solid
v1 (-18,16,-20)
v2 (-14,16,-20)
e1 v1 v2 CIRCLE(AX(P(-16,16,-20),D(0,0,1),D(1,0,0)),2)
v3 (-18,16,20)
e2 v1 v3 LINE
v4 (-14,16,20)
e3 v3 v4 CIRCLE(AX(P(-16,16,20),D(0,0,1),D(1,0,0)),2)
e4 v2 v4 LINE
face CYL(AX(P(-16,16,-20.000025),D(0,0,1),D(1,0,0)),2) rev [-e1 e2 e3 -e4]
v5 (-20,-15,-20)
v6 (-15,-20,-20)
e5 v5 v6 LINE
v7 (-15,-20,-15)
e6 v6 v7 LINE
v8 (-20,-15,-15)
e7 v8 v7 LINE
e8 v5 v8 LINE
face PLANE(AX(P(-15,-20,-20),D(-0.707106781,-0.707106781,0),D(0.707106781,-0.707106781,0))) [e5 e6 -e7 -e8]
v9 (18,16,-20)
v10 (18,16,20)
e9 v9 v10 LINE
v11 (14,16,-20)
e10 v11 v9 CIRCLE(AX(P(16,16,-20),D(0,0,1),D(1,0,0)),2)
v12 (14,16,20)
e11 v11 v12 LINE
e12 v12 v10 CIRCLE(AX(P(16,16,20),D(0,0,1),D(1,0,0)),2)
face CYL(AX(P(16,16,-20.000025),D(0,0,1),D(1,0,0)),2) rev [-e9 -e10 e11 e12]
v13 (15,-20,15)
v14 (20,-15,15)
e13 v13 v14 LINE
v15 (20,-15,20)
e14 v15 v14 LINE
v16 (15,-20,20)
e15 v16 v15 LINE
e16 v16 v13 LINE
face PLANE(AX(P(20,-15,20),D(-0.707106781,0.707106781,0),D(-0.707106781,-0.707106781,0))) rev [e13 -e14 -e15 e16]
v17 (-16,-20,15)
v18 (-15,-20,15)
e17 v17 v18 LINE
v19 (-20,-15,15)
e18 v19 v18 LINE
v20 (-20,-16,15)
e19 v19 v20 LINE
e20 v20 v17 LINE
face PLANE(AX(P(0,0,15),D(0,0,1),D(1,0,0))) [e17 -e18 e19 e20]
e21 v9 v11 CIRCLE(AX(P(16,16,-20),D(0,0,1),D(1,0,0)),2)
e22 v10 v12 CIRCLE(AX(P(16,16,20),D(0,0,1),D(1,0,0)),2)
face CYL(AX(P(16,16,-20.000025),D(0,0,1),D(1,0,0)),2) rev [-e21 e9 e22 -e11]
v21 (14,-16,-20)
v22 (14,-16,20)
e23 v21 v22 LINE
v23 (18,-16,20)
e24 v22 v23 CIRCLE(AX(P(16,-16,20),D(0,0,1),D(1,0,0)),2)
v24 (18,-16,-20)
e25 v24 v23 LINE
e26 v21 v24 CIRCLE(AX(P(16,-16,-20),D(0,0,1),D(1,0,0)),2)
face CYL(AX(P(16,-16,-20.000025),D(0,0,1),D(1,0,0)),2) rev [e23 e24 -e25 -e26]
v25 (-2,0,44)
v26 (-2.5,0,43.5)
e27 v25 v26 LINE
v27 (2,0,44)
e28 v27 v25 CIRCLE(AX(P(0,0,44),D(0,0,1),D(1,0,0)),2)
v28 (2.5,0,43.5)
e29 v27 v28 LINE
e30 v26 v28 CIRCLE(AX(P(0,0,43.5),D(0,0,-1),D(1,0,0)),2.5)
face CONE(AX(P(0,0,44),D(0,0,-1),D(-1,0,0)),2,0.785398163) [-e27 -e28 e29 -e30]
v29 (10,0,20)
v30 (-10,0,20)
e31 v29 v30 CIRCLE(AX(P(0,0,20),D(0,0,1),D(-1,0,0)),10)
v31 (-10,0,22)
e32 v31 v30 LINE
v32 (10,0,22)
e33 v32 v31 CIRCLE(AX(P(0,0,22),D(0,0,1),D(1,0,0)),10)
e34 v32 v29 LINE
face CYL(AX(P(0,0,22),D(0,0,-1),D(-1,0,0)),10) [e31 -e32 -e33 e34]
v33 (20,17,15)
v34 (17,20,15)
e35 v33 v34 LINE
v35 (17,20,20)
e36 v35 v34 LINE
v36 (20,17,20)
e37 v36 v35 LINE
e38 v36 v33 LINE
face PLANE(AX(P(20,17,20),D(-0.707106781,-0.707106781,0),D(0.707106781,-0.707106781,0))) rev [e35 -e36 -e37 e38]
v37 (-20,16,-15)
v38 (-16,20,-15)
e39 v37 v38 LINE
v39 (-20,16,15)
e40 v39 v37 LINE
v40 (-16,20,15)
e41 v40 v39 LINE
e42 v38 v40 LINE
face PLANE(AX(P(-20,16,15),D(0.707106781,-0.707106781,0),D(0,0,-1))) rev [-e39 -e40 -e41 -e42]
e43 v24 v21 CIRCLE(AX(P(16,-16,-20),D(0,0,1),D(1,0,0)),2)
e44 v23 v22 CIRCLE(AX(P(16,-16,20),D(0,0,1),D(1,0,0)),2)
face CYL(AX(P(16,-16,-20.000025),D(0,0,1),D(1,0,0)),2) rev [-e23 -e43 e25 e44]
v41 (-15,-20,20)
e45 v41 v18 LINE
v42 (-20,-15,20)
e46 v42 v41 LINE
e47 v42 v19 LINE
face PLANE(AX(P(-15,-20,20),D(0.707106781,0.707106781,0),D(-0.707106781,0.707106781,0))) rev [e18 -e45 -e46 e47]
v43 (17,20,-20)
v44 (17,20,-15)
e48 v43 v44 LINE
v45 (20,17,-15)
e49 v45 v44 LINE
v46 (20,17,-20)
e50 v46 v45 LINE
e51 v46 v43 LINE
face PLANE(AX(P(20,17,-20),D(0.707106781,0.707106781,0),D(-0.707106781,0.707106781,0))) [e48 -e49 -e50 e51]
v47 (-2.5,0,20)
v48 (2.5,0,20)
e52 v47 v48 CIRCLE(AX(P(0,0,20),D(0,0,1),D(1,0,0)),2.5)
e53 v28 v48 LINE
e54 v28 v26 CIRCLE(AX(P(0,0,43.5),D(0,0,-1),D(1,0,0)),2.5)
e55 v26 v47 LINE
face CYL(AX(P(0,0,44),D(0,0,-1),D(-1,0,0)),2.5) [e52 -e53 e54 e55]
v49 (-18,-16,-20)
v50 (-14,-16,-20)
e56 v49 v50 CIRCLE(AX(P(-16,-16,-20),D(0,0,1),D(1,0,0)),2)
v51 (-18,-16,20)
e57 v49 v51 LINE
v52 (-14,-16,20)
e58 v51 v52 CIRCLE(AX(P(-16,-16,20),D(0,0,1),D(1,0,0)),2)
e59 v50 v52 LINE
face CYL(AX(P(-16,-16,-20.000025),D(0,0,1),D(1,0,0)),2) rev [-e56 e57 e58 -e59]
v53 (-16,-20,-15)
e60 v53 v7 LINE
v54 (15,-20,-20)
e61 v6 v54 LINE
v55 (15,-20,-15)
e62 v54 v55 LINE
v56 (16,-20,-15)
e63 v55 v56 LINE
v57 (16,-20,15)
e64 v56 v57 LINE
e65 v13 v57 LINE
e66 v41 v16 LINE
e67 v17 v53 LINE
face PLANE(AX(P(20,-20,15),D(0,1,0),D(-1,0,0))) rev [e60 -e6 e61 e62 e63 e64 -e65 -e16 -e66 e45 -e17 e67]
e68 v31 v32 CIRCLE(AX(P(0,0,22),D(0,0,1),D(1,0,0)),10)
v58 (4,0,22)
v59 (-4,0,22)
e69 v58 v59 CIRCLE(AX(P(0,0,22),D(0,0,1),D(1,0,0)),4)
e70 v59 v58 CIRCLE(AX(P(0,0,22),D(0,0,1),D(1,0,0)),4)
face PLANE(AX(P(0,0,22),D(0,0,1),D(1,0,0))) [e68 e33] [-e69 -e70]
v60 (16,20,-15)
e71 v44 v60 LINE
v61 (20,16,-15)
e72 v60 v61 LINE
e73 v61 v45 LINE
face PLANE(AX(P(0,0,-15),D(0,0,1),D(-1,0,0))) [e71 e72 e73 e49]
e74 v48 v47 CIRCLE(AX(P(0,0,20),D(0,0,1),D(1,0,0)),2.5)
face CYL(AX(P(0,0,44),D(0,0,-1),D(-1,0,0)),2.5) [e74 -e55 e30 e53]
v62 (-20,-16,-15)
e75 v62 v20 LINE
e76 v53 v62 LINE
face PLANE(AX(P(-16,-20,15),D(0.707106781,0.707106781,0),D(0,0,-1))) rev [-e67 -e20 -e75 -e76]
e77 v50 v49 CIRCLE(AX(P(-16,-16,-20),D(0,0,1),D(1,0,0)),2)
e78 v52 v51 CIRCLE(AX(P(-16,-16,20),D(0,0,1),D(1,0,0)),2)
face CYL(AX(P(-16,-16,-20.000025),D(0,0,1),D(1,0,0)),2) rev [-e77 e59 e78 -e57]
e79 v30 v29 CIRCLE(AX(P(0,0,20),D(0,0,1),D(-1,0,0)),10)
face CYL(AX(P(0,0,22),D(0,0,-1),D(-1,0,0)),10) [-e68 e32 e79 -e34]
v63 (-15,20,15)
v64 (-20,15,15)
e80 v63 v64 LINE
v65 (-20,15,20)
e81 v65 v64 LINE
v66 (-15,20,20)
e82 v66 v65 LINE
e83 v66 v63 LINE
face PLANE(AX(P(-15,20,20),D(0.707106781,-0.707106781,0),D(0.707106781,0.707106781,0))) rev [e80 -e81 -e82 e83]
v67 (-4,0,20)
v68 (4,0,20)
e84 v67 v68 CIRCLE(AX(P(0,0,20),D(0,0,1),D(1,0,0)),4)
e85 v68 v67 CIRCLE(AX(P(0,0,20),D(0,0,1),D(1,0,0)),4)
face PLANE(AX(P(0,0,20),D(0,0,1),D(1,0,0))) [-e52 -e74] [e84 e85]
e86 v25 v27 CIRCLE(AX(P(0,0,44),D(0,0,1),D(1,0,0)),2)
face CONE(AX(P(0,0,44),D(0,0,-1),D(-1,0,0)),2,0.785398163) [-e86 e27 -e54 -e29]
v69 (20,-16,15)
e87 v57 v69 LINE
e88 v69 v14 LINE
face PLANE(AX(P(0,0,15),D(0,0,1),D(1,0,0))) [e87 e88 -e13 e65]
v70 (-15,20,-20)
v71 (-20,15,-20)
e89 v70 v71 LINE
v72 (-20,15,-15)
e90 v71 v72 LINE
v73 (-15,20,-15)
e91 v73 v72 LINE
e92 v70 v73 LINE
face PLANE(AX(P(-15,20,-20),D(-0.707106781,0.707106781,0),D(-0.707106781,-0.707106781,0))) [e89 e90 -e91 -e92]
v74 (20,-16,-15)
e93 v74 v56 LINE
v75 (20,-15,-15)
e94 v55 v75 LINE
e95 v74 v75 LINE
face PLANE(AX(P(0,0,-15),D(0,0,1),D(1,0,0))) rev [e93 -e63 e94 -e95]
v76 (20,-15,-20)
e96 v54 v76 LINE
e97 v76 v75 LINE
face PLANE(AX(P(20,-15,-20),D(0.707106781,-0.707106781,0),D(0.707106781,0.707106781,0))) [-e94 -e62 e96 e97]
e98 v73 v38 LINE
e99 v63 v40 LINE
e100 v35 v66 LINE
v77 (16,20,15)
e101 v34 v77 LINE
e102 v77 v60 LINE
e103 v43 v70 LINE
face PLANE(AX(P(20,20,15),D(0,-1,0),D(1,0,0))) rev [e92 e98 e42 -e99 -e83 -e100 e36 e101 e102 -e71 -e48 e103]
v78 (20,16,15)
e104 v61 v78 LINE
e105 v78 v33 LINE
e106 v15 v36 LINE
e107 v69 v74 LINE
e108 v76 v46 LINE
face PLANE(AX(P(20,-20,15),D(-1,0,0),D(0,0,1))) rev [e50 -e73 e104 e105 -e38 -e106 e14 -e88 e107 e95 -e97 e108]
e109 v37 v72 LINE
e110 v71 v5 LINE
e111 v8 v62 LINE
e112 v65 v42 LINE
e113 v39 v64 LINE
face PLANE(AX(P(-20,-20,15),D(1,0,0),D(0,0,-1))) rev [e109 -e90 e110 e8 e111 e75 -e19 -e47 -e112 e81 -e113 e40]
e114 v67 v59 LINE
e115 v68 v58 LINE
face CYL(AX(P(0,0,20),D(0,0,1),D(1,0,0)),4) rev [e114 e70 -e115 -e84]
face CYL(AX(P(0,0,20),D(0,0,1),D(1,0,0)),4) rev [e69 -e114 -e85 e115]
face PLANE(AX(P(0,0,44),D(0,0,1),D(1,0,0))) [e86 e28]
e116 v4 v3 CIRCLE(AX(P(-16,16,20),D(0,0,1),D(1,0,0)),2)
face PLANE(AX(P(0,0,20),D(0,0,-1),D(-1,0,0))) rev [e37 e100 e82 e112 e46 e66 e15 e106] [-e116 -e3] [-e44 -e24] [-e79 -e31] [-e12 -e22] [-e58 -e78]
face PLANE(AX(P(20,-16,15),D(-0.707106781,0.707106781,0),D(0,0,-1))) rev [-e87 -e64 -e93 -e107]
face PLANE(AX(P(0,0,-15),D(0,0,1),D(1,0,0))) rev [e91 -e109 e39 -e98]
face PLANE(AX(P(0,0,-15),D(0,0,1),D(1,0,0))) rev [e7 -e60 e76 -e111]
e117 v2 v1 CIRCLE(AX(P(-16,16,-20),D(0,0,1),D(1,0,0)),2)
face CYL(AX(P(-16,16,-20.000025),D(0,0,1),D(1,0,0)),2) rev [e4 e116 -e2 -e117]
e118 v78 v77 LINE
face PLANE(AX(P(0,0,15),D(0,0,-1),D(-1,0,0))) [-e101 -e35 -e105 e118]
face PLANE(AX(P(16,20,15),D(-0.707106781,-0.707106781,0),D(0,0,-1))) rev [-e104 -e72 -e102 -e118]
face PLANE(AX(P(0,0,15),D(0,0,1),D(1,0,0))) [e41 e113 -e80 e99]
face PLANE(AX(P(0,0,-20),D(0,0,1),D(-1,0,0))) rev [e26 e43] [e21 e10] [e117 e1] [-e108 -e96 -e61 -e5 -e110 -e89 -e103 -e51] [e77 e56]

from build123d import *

# Parameters (mm, degrees)
SKETCH1_W           = 40
SKETCH1_H           = 40
BOSS_EXTRUDE1_DEPTH = 15
CHAMFER1_SIZE       = 4
BOSS_EXTRUDE2_DEPTH = 5
SKETCH4_R           = 10
BOSS_EXTRUDE3_DEPTH = 2
SKETCH5_R           = 2.5
BOSS_EXTRUDE4_DEPTH = 22
CUT_EXTRUDE1_START  = -2
SKETCH6_R           = 4
SKETCH6_R_2         = 2.5
CUT_EXTRUDE1_DEPTH  = 2
CHAMFER2_SIZE       = 0.5
SKETCH7_R           = 2
CUT_EXTRUDE2_DEPTH  = 49.989794856


with BuildPart() as part:
    # Sketch1 → Boss-Extrude1 (new, symmetric)
    with BuildSketch(Plane.XY):
        Rectangle(SKETCH1_W, SKETCH1_H)
    extrude(amount=BOSS_EXTRUDE1_DEPTH, both=True)

    # Chamfer1
    chamfer1_edges = [part.edges().sort_by_distance(p)[0] for p in [
        (-20, 20, 0),
        (20, 20, 0),
        (20, -20, 0),
        (-20, -20, 0),
    ]]
    chamfer(chamfer1_edges, length=CHAMFER1_SIZE)

    # Sketch3 → Boss-Extrude2 (add)
    with BuildSketch(Plane.XY.offset(15)):
        Polygon((15, -20), (-15, -20), (-20, -15), (-20, 15), (-15, 20), (17, 20), (20, 17), (20, -15), align=None)
    boss_extrude2 = extrude(amount=BOSS_EXTRUDE2_DEPTH)

    # Mirror1: Boss-Extrude2 across plane
    add(boss_extrude2.mirror(Plane.XY))

    # Sketch4 → Boss-Extrude3 (add)
    with BuildSketch(Plane.XY.offset(20)):
        with Locations(Location((0, 0, 0), (0, 0, 180))):
            Circle(SKETCH4_R)
    extrude(amount=BOSS_EXTRUDE3_DEPTH)

    # Sketch5 → Boss-Extrude4 (add)
    with BuildSketch(Plane.XY.offset(22)):
        Circle(SKETCH5_R)
    extrude(amount=BOSS_EXTRUDE4_DEPTH)

    # Sketch6 → Cut-Extrude1 (cut)
    with BuildSketch(Plane.XY.offset(22).offset(CUT_EXTRUDE1_START)):
        Circle(SKETCH6_R)
        Circle(SKETCH6_R_2, mode=Mode.SUBTRACT)
    extrude(amount=CUT_EXTRUDE1_DEPTH, mode=Mode.SUBTRACT)

    # Chamfer2
    chamfer2_edges = [part.edges().sort_by_distance(p)[0] for p in [
        (-2.5, 0, 44),
    ]]
    chamfer(chamfer2_edges, length=CHAMFER2_SIZE)

    # Sketch7 → Cut-Extrude2 (cut, through all)
    with BuildSketch(Plane.XY.offset(20)):
        with Locations((16, 16)):
            Circle(SKETCH7_R)
        with Locations((16, -16)):
            Circle(SKETCH7_R)
        with Locations((-16, -16)):
            Circle(SKETCH7_R)
        with Locations((-16, 16)):
            Circle(SKETCH7_R)
    extrude(amount=-CUT_EXTRUDE2_DEPTH, mode=Mode.SUBTRACT)


solid = part.part
